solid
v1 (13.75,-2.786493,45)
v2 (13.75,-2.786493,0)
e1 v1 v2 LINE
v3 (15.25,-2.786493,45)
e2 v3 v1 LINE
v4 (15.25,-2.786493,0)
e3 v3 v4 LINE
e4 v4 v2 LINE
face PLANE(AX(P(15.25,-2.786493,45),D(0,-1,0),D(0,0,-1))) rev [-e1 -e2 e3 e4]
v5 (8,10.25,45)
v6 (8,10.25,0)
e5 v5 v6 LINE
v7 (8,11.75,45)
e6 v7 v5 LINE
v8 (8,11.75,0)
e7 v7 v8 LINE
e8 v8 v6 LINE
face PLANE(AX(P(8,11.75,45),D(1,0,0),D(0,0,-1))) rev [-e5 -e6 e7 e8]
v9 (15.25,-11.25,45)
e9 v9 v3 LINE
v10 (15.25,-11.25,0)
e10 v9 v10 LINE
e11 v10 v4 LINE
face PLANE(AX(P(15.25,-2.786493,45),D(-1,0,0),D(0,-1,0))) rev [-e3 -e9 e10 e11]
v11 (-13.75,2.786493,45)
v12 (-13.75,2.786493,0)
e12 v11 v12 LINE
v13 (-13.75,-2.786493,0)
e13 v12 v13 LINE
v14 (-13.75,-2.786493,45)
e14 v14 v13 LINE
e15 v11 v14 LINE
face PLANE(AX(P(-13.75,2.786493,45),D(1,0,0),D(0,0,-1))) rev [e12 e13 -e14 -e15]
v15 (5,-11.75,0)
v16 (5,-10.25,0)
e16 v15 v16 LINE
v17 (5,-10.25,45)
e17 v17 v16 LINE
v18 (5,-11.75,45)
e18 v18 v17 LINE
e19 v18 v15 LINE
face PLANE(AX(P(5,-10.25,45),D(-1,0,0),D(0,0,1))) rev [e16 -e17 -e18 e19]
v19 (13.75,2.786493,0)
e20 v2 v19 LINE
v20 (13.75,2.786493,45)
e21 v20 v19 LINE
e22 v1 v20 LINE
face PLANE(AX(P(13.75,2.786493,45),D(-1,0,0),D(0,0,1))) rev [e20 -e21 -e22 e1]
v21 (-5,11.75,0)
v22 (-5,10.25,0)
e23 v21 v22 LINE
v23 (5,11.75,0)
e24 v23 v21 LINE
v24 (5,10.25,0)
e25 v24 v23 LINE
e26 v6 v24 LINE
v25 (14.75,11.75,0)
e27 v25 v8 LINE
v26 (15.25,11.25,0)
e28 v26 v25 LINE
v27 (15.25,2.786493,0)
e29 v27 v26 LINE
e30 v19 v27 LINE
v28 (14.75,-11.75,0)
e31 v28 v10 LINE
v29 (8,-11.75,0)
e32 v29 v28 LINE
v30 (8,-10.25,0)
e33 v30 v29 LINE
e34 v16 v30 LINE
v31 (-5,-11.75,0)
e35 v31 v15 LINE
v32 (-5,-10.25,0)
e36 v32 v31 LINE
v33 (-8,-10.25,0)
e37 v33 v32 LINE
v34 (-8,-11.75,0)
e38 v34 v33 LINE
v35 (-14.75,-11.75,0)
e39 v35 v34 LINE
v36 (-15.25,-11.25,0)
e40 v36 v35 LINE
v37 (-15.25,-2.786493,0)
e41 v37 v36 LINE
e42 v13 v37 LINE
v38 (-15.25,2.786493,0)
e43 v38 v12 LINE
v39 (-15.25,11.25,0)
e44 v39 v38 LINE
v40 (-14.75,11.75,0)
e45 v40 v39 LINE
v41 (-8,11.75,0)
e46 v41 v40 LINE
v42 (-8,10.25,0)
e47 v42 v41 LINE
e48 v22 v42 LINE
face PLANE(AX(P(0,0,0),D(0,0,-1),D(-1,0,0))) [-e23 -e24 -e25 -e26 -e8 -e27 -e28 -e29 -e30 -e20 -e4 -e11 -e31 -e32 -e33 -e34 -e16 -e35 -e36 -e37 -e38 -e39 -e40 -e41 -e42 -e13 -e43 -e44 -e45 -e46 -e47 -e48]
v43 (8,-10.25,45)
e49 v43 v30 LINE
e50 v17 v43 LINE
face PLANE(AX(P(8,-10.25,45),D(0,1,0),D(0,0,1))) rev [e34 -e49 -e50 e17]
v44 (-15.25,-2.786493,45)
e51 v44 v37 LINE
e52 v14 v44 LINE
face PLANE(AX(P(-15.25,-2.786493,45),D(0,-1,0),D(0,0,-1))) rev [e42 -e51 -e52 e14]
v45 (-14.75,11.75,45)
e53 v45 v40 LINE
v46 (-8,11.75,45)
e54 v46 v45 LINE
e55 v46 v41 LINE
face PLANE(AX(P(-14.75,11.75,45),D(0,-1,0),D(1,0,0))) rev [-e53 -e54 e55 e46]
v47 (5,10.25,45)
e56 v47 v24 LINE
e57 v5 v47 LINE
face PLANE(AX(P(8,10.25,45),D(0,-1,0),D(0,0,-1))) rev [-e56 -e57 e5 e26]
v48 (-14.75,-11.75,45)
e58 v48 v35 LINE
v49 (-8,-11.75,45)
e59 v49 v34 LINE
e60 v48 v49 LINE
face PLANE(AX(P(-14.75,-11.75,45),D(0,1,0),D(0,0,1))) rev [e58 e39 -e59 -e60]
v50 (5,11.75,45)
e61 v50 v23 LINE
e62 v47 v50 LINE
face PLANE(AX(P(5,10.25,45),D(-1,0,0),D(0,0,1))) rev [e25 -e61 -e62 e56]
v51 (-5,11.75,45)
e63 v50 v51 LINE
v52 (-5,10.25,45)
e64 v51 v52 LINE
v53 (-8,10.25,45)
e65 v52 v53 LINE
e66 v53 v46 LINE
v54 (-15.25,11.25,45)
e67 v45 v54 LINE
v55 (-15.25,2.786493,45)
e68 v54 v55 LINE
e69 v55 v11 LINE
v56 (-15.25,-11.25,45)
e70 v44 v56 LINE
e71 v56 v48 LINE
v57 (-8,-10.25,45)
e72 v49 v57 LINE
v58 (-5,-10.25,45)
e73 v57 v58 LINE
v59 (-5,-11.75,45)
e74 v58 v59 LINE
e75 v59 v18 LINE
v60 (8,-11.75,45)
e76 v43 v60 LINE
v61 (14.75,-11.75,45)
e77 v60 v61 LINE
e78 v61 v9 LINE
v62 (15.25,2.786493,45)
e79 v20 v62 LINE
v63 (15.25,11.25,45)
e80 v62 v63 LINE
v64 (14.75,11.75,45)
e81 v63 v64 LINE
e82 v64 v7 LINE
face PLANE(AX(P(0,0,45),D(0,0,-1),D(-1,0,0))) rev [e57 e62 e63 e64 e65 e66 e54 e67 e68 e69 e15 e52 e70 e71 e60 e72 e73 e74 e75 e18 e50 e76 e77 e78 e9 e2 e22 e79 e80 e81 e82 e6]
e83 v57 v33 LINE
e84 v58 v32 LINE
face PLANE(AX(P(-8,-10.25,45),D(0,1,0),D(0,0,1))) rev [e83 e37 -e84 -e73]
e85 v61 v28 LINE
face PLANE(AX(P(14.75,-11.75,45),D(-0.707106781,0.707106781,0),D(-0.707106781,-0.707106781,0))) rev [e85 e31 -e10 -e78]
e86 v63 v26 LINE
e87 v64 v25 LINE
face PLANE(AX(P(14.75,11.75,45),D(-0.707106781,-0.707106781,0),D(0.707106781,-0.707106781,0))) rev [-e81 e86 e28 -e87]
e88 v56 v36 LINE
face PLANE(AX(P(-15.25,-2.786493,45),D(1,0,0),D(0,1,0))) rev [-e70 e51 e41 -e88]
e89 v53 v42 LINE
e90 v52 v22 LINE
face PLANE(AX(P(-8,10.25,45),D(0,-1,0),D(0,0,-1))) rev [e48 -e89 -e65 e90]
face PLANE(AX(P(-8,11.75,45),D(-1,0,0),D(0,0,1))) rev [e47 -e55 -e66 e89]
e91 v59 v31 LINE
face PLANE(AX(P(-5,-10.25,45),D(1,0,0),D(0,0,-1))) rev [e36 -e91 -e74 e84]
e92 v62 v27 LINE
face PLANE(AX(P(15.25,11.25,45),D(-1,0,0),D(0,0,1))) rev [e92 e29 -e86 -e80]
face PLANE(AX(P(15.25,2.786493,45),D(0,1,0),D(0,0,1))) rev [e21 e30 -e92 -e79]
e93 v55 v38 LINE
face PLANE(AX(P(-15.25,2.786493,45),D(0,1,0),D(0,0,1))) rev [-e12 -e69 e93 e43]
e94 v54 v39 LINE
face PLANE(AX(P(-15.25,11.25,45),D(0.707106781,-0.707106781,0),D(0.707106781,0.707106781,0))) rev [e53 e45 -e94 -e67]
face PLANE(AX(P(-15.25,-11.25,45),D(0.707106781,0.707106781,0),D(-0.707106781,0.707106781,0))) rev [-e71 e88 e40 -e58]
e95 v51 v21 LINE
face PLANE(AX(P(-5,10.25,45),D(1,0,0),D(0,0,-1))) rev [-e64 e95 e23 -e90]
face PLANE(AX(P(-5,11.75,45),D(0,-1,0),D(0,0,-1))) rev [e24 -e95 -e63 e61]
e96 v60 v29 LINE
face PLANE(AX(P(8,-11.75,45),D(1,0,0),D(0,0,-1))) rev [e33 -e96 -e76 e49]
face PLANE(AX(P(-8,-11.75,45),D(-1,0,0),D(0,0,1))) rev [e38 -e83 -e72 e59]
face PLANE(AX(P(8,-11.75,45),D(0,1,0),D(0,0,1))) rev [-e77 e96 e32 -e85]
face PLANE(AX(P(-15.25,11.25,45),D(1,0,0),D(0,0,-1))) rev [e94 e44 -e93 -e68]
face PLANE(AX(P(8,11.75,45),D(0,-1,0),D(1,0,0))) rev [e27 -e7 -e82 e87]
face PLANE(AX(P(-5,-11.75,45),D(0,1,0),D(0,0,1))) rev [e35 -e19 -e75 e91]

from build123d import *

# Parameters (mm, degrees)
BOSS_EXTRUDE2_DEPTH = 45


with BuildPart() as part:
    # Sketch1 → Boss-Extrude2 (new body)
    with BuildSketch(Plane.XY):
        Polygon((-15.25, 11.25), (-14.75, 11.75), (-8, 11.75), (-8, 10.25), (-5, 10.25), (-5, 11.75), (5, 11.75), (5, 10.25), (8, 10.25), (8, 11.75), (14.75, 11.75), (15.25, 11.25), (15.25, 2.78649269), (13.75, 2.78649269), (13.75, -2.78649269), (15.25, -2.78649269), (15.25, -11.25), (14.75, -11.75), (8, -11.75), (8, -10.25), (5, -10.25), (5, -11.75), (-5, -11.75), (-5, -10.25), (-8, -10.25), (-8, -11.75), (-14.75, -11.75), (-15.25, -11.25), (-15.25, -2.78649269), (-13.75, -2.78649269), (-13.75, 2.78649269), (-15.25, 2.78649269), align=None)
    extrude(amount=BOSS_EXTRUDE2_DEPTH)


solid = part.part
